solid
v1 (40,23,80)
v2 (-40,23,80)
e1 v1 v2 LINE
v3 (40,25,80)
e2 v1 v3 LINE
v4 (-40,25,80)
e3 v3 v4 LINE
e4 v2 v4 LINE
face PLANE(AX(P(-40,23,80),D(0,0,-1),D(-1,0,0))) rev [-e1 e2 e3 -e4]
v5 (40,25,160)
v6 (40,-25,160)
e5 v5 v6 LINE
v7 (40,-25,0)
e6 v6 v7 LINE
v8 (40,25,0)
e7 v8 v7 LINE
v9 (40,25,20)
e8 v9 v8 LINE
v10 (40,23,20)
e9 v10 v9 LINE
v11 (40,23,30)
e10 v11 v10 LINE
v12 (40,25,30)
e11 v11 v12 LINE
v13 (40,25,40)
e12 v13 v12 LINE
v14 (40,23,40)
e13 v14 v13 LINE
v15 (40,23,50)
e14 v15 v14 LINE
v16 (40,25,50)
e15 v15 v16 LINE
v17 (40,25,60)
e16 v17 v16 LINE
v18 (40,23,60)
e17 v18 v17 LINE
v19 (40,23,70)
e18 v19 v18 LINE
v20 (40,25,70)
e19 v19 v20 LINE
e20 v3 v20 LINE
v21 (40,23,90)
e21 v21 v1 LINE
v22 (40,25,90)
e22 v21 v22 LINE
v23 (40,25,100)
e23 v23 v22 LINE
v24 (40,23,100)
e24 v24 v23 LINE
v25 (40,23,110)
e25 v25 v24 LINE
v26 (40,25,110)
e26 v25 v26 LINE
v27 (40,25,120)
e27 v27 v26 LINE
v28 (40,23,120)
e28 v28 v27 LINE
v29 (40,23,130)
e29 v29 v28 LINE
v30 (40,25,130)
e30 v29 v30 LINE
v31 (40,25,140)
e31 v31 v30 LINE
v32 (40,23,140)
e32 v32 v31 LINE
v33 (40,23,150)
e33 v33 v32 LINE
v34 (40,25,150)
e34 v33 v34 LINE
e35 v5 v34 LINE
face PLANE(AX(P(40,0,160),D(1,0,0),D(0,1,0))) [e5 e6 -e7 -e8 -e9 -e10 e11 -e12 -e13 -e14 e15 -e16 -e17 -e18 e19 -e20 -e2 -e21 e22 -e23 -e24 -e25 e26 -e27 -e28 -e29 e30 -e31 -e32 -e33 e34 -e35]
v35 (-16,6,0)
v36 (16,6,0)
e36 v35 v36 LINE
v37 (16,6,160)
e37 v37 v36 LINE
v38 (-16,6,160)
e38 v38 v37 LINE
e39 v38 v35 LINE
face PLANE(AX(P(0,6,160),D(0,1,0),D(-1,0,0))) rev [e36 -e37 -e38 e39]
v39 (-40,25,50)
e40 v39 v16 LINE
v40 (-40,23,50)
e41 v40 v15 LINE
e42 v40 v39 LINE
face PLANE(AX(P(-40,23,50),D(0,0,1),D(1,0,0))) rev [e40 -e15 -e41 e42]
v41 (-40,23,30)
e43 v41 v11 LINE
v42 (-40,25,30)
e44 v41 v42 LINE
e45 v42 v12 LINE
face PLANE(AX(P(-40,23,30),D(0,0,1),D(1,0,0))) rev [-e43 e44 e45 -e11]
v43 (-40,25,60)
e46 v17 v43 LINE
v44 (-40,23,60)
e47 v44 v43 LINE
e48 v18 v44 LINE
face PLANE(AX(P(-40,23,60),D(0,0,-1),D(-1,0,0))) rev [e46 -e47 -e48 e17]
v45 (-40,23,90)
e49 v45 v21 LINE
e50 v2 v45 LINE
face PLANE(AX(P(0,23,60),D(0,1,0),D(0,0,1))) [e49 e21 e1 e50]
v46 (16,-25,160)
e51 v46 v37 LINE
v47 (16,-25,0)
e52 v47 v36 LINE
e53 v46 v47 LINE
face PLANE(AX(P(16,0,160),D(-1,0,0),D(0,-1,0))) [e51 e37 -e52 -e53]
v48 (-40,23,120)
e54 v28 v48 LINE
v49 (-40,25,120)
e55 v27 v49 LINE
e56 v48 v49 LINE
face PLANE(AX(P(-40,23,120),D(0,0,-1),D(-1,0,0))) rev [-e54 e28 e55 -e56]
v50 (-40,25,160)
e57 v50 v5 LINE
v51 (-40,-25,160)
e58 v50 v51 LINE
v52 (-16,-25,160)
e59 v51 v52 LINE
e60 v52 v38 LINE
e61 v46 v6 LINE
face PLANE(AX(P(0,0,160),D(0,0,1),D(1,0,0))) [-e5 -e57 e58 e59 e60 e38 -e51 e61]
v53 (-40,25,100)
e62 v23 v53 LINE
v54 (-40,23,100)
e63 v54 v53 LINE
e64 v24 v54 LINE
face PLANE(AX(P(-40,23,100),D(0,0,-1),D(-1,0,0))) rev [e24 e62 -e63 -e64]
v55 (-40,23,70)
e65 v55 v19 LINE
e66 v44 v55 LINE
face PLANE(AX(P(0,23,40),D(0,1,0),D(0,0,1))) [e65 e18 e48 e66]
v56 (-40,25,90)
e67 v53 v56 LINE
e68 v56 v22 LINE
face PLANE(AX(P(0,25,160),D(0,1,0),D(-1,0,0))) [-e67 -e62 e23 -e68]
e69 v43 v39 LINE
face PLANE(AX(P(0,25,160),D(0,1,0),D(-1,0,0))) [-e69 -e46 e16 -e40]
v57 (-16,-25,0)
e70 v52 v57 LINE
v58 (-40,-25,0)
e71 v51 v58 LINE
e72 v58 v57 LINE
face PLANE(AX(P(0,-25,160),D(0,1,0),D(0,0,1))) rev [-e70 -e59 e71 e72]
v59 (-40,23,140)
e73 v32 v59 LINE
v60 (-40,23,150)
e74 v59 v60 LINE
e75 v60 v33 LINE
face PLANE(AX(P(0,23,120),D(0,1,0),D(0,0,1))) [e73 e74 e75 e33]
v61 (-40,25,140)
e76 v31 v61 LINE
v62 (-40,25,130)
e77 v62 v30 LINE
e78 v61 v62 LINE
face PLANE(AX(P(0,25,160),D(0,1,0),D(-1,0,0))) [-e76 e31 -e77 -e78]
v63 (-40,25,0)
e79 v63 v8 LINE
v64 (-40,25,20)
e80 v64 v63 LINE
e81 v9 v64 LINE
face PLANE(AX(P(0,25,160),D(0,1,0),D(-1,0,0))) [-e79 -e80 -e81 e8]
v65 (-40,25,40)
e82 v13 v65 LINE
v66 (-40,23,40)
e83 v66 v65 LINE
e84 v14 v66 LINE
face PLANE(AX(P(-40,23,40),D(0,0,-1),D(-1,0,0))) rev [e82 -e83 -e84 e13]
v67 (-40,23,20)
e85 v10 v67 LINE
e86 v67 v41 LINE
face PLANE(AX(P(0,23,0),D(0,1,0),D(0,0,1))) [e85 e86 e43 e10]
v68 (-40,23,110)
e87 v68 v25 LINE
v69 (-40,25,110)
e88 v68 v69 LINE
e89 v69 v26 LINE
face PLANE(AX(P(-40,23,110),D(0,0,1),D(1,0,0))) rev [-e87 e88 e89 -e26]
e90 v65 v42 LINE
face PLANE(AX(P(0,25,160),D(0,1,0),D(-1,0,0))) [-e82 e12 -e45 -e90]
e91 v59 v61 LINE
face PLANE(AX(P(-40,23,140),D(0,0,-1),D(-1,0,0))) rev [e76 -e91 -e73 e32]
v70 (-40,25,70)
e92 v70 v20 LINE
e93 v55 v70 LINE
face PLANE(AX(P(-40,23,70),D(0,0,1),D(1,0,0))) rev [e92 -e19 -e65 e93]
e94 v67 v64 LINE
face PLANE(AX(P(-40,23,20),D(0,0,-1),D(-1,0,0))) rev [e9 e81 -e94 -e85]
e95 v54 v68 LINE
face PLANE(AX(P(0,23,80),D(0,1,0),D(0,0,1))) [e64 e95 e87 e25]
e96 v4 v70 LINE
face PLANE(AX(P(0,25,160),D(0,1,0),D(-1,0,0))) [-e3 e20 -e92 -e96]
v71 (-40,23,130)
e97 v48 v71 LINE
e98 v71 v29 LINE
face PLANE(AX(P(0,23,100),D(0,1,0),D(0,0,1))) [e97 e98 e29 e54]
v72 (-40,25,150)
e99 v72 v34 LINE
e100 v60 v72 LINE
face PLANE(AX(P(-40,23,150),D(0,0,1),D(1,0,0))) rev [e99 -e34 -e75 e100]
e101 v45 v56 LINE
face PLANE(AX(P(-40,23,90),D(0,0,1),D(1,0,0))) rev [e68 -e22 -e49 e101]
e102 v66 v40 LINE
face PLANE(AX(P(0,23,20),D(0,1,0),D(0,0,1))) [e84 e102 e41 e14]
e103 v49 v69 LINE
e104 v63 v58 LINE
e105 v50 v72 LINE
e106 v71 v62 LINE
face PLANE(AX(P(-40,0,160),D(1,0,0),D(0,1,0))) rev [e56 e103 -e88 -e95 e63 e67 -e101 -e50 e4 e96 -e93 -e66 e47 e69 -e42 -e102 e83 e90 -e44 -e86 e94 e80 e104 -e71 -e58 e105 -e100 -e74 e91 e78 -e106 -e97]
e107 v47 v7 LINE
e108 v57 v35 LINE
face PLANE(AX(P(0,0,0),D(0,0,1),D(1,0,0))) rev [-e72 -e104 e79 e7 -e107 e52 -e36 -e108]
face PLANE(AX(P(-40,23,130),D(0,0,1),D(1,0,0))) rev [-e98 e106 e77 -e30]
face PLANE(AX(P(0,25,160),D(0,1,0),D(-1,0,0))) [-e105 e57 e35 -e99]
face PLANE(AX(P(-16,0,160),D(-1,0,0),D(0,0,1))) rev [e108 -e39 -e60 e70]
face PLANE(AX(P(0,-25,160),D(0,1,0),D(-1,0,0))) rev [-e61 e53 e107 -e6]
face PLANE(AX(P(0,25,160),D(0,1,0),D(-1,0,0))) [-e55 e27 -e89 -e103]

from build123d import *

# Parameters (mm, degrees)
BOSS_EXTRUDE1_DEPTH = 160
SKETCH2_W           = 80
SKETCH2_H           = 10
CUT_EXTRUDE1_DEPTH  = 2
LPATTERN1_COUNT     = 8
LPATTERN1_PITCH     = 20


with BuildPart() as part:
    # Sketch1 → Boss-Extrude1 (new body)
    with BuildSketch(Plane.XY):
        Polygon((0, 6), (0, 25), (-40, 25), (-40, -25), (-16, -25), (-16, 6), align=None)
        Polygon((40, 25), (0, 25), (0, 6), (16, 6), (16, -25), (40, -25), align=None)
    extrude(amount=BOSS_EXTRUDE1_DEPTH)

    # Sketch2 → Cut-Extrude1 (cut)
    with BuildSketch(Plane(origin=(0, 25, 0), x_dir=(1, 0, 0), z_dir=(0, 1, 0))):
        with Locations((0, -25)):
            Rectangle(SKETCH2_W, SKETCH2_H)
    cut_extrude1 = extrude(amount=-CUT_EXTRUDE1_DEPTH, mode=Mode.SUBTRACT)

    # LPattern1: Cut-Extrude1 ×8
    with Locations(*[(0, 0, i * LPATTERN1_PITCH) for i in range(1, LPATTERN1_COUNT)]):
        add(cut_extrude1, mode=Mode.SUBTRACT)


solid = part.part
